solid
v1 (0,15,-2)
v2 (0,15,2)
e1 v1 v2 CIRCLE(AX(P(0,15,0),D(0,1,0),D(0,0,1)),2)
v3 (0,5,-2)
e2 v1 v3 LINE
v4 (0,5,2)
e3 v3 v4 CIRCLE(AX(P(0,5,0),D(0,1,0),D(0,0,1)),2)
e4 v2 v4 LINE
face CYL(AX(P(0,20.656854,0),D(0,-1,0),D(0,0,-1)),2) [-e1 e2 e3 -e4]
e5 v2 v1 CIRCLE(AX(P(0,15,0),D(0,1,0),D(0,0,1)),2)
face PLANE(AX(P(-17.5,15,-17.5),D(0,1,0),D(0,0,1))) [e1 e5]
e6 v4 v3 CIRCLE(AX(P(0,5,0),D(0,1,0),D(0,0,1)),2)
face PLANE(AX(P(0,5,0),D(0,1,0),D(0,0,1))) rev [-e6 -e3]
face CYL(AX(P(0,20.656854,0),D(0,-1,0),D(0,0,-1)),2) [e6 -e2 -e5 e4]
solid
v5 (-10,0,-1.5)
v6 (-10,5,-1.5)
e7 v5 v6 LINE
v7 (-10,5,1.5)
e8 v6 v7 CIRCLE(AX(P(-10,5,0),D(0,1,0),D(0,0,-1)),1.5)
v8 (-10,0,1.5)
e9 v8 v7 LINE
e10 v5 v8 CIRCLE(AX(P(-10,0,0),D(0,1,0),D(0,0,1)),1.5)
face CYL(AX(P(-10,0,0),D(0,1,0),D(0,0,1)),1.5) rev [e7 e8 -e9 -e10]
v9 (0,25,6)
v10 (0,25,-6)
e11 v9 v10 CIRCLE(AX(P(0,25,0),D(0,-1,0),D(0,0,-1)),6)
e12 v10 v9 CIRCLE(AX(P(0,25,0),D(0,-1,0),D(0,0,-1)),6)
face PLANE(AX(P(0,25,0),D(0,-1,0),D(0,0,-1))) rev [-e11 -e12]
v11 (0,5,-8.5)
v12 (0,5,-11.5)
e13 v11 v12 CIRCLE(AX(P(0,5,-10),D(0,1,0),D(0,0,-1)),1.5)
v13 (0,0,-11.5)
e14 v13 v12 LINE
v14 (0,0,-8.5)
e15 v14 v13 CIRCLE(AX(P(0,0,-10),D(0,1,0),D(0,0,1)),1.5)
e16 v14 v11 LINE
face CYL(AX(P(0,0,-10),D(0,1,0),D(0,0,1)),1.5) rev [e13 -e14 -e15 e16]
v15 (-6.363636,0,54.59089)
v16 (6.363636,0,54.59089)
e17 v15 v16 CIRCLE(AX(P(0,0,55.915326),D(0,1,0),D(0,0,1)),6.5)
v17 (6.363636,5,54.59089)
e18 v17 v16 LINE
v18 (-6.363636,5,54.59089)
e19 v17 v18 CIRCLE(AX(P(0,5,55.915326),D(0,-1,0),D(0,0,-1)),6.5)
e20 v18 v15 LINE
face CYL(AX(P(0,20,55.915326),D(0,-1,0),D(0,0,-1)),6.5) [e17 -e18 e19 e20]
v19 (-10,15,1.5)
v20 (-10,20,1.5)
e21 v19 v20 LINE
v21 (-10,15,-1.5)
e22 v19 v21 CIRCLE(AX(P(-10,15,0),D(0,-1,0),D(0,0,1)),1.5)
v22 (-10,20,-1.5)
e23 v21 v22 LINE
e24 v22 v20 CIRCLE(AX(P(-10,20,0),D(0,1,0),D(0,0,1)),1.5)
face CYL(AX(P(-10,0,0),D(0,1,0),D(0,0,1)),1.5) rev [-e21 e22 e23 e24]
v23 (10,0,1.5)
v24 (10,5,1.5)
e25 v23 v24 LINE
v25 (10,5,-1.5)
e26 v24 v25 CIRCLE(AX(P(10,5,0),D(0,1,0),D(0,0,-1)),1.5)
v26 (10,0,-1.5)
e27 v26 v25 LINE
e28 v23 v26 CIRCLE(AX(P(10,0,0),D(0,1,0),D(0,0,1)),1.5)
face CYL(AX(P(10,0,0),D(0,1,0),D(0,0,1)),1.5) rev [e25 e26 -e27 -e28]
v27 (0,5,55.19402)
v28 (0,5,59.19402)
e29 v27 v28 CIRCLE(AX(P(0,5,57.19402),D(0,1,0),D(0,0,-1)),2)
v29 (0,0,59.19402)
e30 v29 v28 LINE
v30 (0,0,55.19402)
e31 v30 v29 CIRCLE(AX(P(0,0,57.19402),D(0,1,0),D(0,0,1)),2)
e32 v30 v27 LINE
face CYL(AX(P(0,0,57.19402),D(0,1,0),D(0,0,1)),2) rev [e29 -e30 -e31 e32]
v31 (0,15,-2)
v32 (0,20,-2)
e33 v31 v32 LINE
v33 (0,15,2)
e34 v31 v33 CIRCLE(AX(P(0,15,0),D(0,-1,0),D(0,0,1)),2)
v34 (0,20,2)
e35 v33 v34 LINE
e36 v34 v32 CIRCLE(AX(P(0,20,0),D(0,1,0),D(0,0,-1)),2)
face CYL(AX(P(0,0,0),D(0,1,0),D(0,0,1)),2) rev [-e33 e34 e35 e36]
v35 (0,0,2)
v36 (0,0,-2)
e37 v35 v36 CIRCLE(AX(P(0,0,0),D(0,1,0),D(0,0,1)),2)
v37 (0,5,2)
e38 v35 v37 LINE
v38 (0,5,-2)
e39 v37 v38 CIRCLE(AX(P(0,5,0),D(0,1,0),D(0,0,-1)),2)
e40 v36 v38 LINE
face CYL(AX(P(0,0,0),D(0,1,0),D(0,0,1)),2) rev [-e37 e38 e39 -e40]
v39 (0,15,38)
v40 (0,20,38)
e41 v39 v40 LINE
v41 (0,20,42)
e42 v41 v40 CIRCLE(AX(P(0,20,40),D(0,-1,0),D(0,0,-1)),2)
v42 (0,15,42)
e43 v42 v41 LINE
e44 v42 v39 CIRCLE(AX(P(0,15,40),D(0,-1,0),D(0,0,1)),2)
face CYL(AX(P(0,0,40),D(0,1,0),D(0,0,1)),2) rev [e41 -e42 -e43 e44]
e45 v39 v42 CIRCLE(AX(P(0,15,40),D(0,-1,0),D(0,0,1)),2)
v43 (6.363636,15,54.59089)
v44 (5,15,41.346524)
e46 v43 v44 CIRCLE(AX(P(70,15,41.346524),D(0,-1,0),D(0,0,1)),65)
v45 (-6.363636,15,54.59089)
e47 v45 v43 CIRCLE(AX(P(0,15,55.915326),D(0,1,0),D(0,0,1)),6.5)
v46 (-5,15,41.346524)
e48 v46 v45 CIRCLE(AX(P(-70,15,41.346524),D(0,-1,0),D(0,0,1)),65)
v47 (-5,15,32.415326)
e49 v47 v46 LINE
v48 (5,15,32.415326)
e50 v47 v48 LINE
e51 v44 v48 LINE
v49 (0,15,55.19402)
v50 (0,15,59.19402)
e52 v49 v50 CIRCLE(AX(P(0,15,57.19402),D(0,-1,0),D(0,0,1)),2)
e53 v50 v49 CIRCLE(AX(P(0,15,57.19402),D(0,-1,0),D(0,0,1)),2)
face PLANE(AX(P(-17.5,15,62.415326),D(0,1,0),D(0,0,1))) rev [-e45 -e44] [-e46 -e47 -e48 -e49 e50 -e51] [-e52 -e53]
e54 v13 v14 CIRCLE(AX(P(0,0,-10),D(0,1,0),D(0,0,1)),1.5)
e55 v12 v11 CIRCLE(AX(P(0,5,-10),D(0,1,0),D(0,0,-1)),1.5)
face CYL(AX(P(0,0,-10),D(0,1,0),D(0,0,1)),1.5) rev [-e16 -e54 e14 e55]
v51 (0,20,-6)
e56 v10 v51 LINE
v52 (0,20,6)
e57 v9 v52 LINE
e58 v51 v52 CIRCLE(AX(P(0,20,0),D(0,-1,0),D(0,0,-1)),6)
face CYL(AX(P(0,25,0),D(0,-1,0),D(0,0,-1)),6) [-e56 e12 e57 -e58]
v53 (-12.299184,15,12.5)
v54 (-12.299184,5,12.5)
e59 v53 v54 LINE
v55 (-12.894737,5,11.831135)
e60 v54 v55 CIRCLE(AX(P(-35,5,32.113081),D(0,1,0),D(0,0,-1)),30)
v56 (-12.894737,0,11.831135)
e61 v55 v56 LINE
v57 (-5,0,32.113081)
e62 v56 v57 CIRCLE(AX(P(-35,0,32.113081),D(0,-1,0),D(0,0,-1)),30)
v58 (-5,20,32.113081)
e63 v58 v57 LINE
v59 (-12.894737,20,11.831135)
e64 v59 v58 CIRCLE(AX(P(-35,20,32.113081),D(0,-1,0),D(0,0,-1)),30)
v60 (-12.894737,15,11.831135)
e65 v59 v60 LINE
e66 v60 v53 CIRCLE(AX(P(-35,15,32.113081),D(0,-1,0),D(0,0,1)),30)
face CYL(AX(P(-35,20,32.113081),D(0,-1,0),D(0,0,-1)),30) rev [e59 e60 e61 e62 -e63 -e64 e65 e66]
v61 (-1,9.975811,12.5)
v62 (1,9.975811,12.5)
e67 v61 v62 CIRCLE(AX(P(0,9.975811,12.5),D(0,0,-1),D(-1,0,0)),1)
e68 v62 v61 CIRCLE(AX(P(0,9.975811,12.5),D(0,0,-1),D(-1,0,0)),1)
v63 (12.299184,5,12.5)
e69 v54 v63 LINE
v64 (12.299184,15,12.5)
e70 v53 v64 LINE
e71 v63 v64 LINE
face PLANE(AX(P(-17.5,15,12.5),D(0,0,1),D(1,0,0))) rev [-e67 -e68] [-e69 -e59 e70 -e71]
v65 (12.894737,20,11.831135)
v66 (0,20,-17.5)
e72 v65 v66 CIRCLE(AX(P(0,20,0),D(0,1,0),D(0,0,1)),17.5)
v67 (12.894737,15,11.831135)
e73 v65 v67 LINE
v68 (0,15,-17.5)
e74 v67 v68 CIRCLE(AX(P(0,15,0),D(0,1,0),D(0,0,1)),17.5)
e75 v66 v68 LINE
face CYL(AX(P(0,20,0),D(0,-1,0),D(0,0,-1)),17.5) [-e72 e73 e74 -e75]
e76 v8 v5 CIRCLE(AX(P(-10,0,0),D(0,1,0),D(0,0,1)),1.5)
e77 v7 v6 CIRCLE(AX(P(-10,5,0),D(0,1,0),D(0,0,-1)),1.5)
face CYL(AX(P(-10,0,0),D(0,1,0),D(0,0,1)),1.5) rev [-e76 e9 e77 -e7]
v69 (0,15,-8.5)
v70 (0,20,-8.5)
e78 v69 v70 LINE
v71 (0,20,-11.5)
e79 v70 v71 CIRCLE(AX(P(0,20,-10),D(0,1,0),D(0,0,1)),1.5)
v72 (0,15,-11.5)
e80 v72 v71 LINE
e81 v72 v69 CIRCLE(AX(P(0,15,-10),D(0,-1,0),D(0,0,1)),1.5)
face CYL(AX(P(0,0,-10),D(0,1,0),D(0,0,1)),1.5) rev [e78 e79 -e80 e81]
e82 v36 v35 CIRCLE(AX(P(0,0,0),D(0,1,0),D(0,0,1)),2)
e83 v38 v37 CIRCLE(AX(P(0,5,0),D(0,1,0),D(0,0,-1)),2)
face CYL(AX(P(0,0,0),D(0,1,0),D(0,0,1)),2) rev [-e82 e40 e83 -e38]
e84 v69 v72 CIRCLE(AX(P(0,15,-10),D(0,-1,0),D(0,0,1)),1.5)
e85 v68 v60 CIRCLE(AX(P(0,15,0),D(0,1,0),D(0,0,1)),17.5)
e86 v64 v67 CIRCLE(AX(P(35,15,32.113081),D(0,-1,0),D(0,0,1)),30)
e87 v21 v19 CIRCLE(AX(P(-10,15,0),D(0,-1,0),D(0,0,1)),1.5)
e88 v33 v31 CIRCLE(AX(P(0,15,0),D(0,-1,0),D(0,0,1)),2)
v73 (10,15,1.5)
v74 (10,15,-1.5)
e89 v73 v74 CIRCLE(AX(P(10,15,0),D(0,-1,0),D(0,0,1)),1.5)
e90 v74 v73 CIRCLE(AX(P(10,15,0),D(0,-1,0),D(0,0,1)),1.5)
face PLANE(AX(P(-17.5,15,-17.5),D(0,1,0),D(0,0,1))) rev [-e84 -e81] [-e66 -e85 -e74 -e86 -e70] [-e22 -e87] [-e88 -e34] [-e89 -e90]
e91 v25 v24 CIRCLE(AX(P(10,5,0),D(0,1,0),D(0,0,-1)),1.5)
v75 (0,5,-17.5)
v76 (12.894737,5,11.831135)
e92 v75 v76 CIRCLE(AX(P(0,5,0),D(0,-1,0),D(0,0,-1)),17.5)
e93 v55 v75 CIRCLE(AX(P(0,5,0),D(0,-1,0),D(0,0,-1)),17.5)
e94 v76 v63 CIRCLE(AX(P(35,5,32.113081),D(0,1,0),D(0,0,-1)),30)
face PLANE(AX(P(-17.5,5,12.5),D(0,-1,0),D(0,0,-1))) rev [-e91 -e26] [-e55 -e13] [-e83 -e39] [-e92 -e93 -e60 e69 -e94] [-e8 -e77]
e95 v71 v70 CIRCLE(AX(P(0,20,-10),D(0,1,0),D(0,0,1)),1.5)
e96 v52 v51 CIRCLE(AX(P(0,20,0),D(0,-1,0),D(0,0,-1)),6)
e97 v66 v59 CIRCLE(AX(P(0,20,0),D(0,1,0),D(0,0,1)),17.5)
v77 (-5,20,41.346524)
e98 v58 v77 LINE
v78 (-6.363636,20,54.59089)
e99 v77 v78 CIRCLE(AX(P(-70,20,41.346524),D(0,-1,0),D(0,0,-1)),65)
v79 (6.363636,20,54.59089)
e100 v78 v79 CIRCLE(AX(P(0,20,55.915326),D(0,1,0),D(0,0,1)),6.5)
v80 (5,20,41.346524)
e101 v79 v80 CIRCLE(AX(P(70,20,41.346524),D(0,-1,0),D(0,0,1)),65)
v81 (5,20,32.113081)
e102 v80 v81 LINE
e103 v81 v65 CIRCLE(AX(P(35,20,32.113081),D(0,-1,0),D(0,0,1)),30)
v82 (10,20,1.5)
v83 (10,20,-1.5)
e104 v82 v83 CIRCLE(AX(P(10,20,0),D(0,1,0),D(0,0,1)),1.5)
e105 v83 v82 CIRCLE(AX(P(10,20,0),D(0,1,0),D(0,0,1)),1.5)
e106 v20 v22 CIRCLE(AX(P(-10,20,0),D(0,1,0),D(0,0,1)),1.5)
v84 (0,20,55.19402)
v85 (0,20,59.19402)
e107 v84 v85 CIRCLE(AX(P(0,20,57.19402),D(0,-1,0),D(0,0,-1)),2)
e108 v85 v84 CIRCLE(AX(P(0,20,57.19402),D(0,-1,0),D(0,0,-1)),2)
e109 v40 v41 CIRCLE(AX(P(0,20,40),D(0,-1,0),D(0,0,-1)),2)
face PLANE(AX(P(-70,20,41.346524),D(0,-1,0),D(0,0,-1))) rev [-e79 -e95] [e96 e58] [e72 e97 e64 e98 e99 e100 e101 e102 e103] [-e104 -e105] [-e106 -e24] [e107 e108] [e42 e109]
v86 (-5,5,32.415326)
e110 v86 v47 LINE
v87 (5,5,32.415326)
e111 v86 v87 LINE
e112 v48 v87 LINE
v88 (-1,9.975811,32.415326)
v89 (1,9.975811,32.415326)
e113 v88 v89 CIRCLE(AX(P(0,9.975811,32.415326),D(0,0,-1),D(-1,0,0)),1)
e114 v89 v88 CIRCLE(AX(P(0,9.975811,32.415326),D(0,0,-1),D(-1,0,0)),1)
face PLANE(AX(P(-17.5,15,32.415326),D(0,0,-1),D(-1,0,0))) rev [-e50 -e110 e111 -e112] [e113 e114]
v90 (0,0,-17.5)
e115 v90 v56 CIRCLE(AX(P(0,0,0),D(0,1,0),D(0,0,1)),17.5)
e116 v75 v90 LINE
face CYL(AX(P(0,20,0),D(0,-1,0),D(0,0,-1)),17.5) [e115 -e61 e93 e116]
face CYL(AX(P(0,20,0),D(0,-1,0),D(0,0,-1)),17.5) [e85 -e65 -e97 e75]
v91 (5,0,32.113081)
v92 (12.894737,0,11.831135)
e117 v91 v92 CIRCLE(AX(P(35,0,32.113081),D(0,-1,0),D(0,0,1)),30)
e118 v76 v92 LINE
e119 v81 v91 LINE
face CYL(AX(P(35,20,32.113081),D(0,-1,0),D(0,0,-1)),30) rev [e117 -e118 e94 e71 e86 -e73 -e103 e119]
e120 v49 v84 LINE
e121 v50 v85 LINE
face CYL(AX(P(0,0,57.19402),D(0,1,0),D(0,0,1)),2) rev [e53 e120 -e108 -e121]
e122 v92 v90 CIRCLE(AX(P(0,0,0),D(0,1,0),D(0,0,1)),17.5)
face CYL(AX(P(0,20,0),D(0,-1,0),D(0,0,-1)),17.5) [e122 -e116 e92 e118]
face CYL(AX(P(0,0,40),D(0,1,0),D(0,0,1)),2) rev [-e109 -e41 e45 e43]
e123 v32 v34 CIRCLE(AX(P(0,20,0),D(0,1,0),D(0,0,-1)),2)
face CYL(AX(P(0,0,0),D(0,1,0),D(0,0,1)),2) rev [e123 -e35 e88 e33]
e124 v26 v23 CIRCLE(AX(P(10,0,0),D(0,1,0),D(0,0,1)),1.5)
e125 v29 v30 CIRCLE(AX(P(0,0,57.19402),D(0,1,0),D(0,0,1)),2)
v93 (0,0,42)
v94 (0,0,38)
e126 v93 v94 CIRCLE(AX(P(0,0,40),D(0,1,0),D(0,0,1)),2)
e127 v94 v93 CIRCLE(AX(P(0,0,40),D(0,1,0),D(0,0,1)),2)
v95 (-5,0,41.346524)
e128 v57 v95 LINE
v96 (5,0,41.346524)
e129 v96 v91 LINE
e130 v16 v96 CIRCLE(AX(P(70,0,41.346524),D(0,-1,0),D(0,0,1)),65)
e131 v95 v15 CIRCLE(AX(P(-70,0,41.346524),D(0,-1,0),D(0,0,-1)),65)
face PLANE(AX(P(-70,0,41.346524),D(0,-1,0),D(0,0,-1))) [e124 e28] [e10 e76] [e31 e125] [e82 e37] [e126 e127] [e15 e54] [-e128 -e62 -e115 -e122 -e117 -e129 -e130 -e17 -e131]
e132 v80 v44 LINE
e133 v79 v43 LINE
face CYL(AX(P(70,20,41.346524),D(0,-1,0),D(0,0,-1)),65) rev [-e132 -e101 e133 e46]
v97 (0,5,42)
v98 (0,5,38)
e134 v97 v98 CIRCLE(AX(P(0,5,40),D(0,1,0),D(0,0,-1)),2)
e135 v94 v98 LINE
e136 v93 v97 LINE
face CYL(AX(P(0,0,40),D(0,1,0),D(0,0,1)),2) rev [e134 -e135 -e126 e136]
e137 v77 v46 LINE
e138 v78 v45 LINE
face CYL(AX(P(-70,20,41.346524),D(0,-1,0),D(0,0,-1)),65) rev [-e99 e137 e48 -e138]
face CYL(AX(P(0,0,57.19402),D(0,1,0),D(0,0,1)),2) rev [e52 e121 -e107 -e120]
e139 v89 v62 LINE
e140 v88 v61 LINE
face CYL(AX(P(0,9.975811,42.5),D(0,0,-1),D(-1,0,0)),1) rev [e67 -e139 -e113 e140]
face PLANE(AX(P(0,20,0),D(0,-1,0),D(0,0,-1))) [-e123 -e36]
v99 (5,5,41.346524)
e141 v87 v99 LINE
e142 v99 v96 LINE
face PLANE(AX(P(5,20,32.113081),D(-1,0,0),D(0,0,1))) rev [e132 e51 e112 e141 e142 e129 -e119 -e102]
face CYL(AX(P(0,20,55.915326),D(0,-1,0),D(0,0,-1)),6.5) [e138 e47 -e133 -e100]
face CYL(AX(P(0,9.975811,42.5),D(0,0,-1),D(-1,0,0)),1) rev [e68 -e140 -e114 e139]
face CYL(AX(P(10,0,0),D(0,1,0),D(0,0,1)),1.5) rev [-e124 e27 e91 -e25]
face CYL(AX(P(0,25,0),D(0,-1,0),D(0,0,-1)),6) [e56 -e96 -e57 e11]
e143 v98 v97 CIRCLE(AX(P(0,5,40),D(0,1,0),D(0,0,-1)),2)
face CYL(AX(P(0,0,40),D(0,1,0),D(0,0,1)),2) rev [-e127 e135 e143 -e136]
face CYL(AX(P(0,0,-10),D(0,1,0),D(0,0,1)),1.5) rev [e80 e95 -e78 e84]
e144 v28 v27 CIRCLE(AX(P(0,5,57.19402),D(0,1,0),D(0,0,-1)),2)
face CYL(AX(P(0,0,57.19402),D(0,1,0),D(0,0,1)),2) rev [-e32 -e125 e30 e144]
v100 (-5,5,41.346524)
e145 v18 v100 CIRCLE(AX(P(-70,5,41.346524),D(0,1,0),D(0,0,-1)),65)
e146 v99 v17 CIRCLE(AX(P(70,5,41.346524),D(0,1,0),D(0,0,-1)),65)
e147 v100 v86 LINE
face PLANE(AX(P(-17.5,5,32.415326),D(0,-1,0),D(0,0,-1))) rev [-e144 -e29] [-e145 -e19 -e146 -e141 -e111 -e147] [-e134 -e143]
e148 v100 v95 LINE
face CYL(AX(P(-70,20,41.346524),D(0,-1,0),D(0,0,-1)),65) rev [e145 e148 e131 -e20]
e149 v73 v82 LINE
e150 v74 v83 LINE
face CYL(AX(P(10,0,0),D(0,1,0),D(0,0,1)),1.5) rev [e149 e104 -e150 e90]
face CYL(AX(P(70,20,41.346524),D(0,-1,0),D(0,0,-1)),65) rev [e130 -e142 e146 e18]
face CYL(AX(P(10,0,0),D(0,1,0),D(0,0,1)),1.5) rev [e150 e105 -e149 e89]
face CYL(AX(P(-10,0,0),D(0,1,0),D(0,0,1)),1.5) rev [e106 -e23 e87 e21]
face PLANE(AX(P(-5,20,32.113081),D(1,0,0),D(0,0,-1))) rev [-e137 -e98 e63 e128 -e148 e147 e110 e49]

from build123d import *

# Parameters (mm, degrees)
BOSS_EXTRUDE1_DEPTH     = 20
CUT_EXTRUDE1_DEPTH      = 68.837474407
CUT_EXTRUDE1_DEPTH_BACK = 68.837474407
SKETCH2_R               = 2
SKETCH3_R               = 2
CUT_EXTRUDE2_DEPTH      = 68.837474407
SKETCH4_R               = 1.5
CUT_EXTRUDE3_DEPTH      = 68.837474407
CUT_EXTRUDE4_DEPTH      = 68.837474407
CUT_EXTRUDE4_DEPTH_BACK = 68.837474407
SKETCH5_W               = 30
SKETCH5_H               = 10
BOSS_EXTRUDE2_START     = -20
SKETCH6_R               = 6
BOSS_EXTRUDE2_DEPTH     = 5
SKETCH7_R               = 2
BOSS_EXTRUDE4_DEPTH     = 10
SKETCH8_R               = 1
CUT_EXTRUDE5_DEPTH      = 30


with BuildPart() as part:
    # Sketch1 → Boss-Extrude1 (new body)
    with BuildSketch(Plane(origin=(0, 0, 0), x_dir=(1, 0, 0), z_dir=(0, 1, 0))):
        with BuildLine():
            Line((-5, -32.113081447), (-5, -41.34652383))
            ThreePointArc((-5, -41.34652383), (-5.341807803, -48.003714064), (-6.363636364, -54.590889543))
            ThreePointArc((-6.363636364, -54.590889543), (0, -62.415326114), (6.363636364, -54.590889543))
            ThreePointArc((6.363636364, -54.590889543), (5.341807803, -48.003714064), (5, -41.34652383))
            Line((5, -41.34652383), (5, -32.113081447))
            ThreePointArc((5, -32.113081447), (7.043266511, -21.230937695), (12.894736842, -11.83113527))
            ThreePointArc((12.894736842, -11.83113527), (0, 17.5), (-12.894736842, -11.83113527))
            ThreePointArc((-12.894736842, -11.83113527), (-7.043266511, -21.230937695), (-5, -32.113081447))
        make_face()
    extrude(amount=BOSS_EXTRUDE1_DEPTH)

    # Sketch2 → Cut-Extrude1 (cut, two sides: drawn at the far end of the back side and taken through both)
    with BuildSketch(Plane(origin=(0, 20, 0), x_dir=(1, 0, 0), z_dir=(0, 1, 0)).offset(-CUT_EXTRUDE1_DEPTH_BACK)):
        with Locations(Location((0, -40, 0), (0, 0, 270))):
            Circle(SKETCH2_R)
        with Locations(Location((0, -57.194020253, 0), (0, 0, 270))):
            Circle(SKETCH2_R)
    extrude(amount=CUT_EXTRUDE1_DEPTH + CUT_EXTRUDE1_DEPTH_BACK, mode=Mode.SUBTRACT)

    # Sketch3 → Cut-Extrude2 (cut, through all)
    with BuildSketch(Plane(origin=(0, 20, 0), x_dir=(1, 0, 0), z_dir=(0, 1, 0))):
        with Locations(Location((0, 0, 0), (0, 0, 270))):
            Circle(SKETCH3_R)
    extrude(amount=-CUT_EXTRUDE2_DEPTH, mode=Mode.SUBTRACT)

    # Sketch4 → Cut-Extrude3 (cut, through all)
    with BuildSketch(Plane(origin=(0, 20, 0), x_dir=(1, 0, 0), z_dir=(0, 1, 0))):
        with Locations(Location((-10, 0, 0), (0, 0, 270))):
            Circle(SKETCH4_R)
        with Locations(Location((10, 0, 0), (0, 0, 270))):
            Circle(SKETCH4_R)
        with Locations(Location((0, 10, 0), (0, 0, 270))):
            Circle(SKETCH4_R)
    extrude(amount=-CUT_EXTRUDE3_DEPTH, mode=Mode.SUBTRACT)

    # Sketch5 → Cut-Extrude4 (cut, two sides: drawn at the far end of the back side and taken through both)
    with BuildSketch(Plane(origin=(0, 0, 0), x_dir=(0, 0, -1), z_dir=(1, 0, 0)).offset(-CUT_EXTRUDE4_DEPTH_BACK)):
        with Locations((-47.415326114, 10)):
            Rectangle(SKETCH5_W, SKETCH5_H)
        with Locations((2.5, 10)):
            Rectangle(SKETCH5_W, SKETCH5_H)
    extrude(amount=CUT_EXTRUDE4_DEPTH + CUT_EXTRUDE4_DEPTH_BACK, mode=Mode.SUBTRACT)

    # Sketch6 → Boss-Extrude2 (add)
    with BuildSketch(Plane.XZ.offset(BOSS_EXTRUDE2_START)):
        with Locations(Location((0, 0, 0), (0, 0, 270))):
            Circle(SKETCH6_R)
    extrude(amount=-BOSS_EXTRUDE2_DEPTH)

    # Sketch8 → Cut-Extrude5 (cut)
    with BuildSketch(Plane(origin=(0, 0, 12.5), x_dir=(-1, 0, 0), z_dir=(0, 0, -1))):
        with Locations((0, 9.975810979)):
            Circle(SKETCH8_R)
    extrude(amount=-CUT_EXTRUDE5_DEPTH, mode=Mode.SUBTRACT)


with BuildPart() as body_2:
    # Sketch7 → Boss-Extrude4 (new body)
    with BuildSketch(Plane(origin=(0, 5, 0), x_dir=(1, 0, 0), z_dir=(0, 1, 0))):
        with Locations(Location((0, 0, 0), (0, 0, 270))):
            Circle(SKETCH7_R)
    extrude(amount=BOSS_EXTRUDE4_DEPTH)


solid = Compound([part.part, body_2.part])
